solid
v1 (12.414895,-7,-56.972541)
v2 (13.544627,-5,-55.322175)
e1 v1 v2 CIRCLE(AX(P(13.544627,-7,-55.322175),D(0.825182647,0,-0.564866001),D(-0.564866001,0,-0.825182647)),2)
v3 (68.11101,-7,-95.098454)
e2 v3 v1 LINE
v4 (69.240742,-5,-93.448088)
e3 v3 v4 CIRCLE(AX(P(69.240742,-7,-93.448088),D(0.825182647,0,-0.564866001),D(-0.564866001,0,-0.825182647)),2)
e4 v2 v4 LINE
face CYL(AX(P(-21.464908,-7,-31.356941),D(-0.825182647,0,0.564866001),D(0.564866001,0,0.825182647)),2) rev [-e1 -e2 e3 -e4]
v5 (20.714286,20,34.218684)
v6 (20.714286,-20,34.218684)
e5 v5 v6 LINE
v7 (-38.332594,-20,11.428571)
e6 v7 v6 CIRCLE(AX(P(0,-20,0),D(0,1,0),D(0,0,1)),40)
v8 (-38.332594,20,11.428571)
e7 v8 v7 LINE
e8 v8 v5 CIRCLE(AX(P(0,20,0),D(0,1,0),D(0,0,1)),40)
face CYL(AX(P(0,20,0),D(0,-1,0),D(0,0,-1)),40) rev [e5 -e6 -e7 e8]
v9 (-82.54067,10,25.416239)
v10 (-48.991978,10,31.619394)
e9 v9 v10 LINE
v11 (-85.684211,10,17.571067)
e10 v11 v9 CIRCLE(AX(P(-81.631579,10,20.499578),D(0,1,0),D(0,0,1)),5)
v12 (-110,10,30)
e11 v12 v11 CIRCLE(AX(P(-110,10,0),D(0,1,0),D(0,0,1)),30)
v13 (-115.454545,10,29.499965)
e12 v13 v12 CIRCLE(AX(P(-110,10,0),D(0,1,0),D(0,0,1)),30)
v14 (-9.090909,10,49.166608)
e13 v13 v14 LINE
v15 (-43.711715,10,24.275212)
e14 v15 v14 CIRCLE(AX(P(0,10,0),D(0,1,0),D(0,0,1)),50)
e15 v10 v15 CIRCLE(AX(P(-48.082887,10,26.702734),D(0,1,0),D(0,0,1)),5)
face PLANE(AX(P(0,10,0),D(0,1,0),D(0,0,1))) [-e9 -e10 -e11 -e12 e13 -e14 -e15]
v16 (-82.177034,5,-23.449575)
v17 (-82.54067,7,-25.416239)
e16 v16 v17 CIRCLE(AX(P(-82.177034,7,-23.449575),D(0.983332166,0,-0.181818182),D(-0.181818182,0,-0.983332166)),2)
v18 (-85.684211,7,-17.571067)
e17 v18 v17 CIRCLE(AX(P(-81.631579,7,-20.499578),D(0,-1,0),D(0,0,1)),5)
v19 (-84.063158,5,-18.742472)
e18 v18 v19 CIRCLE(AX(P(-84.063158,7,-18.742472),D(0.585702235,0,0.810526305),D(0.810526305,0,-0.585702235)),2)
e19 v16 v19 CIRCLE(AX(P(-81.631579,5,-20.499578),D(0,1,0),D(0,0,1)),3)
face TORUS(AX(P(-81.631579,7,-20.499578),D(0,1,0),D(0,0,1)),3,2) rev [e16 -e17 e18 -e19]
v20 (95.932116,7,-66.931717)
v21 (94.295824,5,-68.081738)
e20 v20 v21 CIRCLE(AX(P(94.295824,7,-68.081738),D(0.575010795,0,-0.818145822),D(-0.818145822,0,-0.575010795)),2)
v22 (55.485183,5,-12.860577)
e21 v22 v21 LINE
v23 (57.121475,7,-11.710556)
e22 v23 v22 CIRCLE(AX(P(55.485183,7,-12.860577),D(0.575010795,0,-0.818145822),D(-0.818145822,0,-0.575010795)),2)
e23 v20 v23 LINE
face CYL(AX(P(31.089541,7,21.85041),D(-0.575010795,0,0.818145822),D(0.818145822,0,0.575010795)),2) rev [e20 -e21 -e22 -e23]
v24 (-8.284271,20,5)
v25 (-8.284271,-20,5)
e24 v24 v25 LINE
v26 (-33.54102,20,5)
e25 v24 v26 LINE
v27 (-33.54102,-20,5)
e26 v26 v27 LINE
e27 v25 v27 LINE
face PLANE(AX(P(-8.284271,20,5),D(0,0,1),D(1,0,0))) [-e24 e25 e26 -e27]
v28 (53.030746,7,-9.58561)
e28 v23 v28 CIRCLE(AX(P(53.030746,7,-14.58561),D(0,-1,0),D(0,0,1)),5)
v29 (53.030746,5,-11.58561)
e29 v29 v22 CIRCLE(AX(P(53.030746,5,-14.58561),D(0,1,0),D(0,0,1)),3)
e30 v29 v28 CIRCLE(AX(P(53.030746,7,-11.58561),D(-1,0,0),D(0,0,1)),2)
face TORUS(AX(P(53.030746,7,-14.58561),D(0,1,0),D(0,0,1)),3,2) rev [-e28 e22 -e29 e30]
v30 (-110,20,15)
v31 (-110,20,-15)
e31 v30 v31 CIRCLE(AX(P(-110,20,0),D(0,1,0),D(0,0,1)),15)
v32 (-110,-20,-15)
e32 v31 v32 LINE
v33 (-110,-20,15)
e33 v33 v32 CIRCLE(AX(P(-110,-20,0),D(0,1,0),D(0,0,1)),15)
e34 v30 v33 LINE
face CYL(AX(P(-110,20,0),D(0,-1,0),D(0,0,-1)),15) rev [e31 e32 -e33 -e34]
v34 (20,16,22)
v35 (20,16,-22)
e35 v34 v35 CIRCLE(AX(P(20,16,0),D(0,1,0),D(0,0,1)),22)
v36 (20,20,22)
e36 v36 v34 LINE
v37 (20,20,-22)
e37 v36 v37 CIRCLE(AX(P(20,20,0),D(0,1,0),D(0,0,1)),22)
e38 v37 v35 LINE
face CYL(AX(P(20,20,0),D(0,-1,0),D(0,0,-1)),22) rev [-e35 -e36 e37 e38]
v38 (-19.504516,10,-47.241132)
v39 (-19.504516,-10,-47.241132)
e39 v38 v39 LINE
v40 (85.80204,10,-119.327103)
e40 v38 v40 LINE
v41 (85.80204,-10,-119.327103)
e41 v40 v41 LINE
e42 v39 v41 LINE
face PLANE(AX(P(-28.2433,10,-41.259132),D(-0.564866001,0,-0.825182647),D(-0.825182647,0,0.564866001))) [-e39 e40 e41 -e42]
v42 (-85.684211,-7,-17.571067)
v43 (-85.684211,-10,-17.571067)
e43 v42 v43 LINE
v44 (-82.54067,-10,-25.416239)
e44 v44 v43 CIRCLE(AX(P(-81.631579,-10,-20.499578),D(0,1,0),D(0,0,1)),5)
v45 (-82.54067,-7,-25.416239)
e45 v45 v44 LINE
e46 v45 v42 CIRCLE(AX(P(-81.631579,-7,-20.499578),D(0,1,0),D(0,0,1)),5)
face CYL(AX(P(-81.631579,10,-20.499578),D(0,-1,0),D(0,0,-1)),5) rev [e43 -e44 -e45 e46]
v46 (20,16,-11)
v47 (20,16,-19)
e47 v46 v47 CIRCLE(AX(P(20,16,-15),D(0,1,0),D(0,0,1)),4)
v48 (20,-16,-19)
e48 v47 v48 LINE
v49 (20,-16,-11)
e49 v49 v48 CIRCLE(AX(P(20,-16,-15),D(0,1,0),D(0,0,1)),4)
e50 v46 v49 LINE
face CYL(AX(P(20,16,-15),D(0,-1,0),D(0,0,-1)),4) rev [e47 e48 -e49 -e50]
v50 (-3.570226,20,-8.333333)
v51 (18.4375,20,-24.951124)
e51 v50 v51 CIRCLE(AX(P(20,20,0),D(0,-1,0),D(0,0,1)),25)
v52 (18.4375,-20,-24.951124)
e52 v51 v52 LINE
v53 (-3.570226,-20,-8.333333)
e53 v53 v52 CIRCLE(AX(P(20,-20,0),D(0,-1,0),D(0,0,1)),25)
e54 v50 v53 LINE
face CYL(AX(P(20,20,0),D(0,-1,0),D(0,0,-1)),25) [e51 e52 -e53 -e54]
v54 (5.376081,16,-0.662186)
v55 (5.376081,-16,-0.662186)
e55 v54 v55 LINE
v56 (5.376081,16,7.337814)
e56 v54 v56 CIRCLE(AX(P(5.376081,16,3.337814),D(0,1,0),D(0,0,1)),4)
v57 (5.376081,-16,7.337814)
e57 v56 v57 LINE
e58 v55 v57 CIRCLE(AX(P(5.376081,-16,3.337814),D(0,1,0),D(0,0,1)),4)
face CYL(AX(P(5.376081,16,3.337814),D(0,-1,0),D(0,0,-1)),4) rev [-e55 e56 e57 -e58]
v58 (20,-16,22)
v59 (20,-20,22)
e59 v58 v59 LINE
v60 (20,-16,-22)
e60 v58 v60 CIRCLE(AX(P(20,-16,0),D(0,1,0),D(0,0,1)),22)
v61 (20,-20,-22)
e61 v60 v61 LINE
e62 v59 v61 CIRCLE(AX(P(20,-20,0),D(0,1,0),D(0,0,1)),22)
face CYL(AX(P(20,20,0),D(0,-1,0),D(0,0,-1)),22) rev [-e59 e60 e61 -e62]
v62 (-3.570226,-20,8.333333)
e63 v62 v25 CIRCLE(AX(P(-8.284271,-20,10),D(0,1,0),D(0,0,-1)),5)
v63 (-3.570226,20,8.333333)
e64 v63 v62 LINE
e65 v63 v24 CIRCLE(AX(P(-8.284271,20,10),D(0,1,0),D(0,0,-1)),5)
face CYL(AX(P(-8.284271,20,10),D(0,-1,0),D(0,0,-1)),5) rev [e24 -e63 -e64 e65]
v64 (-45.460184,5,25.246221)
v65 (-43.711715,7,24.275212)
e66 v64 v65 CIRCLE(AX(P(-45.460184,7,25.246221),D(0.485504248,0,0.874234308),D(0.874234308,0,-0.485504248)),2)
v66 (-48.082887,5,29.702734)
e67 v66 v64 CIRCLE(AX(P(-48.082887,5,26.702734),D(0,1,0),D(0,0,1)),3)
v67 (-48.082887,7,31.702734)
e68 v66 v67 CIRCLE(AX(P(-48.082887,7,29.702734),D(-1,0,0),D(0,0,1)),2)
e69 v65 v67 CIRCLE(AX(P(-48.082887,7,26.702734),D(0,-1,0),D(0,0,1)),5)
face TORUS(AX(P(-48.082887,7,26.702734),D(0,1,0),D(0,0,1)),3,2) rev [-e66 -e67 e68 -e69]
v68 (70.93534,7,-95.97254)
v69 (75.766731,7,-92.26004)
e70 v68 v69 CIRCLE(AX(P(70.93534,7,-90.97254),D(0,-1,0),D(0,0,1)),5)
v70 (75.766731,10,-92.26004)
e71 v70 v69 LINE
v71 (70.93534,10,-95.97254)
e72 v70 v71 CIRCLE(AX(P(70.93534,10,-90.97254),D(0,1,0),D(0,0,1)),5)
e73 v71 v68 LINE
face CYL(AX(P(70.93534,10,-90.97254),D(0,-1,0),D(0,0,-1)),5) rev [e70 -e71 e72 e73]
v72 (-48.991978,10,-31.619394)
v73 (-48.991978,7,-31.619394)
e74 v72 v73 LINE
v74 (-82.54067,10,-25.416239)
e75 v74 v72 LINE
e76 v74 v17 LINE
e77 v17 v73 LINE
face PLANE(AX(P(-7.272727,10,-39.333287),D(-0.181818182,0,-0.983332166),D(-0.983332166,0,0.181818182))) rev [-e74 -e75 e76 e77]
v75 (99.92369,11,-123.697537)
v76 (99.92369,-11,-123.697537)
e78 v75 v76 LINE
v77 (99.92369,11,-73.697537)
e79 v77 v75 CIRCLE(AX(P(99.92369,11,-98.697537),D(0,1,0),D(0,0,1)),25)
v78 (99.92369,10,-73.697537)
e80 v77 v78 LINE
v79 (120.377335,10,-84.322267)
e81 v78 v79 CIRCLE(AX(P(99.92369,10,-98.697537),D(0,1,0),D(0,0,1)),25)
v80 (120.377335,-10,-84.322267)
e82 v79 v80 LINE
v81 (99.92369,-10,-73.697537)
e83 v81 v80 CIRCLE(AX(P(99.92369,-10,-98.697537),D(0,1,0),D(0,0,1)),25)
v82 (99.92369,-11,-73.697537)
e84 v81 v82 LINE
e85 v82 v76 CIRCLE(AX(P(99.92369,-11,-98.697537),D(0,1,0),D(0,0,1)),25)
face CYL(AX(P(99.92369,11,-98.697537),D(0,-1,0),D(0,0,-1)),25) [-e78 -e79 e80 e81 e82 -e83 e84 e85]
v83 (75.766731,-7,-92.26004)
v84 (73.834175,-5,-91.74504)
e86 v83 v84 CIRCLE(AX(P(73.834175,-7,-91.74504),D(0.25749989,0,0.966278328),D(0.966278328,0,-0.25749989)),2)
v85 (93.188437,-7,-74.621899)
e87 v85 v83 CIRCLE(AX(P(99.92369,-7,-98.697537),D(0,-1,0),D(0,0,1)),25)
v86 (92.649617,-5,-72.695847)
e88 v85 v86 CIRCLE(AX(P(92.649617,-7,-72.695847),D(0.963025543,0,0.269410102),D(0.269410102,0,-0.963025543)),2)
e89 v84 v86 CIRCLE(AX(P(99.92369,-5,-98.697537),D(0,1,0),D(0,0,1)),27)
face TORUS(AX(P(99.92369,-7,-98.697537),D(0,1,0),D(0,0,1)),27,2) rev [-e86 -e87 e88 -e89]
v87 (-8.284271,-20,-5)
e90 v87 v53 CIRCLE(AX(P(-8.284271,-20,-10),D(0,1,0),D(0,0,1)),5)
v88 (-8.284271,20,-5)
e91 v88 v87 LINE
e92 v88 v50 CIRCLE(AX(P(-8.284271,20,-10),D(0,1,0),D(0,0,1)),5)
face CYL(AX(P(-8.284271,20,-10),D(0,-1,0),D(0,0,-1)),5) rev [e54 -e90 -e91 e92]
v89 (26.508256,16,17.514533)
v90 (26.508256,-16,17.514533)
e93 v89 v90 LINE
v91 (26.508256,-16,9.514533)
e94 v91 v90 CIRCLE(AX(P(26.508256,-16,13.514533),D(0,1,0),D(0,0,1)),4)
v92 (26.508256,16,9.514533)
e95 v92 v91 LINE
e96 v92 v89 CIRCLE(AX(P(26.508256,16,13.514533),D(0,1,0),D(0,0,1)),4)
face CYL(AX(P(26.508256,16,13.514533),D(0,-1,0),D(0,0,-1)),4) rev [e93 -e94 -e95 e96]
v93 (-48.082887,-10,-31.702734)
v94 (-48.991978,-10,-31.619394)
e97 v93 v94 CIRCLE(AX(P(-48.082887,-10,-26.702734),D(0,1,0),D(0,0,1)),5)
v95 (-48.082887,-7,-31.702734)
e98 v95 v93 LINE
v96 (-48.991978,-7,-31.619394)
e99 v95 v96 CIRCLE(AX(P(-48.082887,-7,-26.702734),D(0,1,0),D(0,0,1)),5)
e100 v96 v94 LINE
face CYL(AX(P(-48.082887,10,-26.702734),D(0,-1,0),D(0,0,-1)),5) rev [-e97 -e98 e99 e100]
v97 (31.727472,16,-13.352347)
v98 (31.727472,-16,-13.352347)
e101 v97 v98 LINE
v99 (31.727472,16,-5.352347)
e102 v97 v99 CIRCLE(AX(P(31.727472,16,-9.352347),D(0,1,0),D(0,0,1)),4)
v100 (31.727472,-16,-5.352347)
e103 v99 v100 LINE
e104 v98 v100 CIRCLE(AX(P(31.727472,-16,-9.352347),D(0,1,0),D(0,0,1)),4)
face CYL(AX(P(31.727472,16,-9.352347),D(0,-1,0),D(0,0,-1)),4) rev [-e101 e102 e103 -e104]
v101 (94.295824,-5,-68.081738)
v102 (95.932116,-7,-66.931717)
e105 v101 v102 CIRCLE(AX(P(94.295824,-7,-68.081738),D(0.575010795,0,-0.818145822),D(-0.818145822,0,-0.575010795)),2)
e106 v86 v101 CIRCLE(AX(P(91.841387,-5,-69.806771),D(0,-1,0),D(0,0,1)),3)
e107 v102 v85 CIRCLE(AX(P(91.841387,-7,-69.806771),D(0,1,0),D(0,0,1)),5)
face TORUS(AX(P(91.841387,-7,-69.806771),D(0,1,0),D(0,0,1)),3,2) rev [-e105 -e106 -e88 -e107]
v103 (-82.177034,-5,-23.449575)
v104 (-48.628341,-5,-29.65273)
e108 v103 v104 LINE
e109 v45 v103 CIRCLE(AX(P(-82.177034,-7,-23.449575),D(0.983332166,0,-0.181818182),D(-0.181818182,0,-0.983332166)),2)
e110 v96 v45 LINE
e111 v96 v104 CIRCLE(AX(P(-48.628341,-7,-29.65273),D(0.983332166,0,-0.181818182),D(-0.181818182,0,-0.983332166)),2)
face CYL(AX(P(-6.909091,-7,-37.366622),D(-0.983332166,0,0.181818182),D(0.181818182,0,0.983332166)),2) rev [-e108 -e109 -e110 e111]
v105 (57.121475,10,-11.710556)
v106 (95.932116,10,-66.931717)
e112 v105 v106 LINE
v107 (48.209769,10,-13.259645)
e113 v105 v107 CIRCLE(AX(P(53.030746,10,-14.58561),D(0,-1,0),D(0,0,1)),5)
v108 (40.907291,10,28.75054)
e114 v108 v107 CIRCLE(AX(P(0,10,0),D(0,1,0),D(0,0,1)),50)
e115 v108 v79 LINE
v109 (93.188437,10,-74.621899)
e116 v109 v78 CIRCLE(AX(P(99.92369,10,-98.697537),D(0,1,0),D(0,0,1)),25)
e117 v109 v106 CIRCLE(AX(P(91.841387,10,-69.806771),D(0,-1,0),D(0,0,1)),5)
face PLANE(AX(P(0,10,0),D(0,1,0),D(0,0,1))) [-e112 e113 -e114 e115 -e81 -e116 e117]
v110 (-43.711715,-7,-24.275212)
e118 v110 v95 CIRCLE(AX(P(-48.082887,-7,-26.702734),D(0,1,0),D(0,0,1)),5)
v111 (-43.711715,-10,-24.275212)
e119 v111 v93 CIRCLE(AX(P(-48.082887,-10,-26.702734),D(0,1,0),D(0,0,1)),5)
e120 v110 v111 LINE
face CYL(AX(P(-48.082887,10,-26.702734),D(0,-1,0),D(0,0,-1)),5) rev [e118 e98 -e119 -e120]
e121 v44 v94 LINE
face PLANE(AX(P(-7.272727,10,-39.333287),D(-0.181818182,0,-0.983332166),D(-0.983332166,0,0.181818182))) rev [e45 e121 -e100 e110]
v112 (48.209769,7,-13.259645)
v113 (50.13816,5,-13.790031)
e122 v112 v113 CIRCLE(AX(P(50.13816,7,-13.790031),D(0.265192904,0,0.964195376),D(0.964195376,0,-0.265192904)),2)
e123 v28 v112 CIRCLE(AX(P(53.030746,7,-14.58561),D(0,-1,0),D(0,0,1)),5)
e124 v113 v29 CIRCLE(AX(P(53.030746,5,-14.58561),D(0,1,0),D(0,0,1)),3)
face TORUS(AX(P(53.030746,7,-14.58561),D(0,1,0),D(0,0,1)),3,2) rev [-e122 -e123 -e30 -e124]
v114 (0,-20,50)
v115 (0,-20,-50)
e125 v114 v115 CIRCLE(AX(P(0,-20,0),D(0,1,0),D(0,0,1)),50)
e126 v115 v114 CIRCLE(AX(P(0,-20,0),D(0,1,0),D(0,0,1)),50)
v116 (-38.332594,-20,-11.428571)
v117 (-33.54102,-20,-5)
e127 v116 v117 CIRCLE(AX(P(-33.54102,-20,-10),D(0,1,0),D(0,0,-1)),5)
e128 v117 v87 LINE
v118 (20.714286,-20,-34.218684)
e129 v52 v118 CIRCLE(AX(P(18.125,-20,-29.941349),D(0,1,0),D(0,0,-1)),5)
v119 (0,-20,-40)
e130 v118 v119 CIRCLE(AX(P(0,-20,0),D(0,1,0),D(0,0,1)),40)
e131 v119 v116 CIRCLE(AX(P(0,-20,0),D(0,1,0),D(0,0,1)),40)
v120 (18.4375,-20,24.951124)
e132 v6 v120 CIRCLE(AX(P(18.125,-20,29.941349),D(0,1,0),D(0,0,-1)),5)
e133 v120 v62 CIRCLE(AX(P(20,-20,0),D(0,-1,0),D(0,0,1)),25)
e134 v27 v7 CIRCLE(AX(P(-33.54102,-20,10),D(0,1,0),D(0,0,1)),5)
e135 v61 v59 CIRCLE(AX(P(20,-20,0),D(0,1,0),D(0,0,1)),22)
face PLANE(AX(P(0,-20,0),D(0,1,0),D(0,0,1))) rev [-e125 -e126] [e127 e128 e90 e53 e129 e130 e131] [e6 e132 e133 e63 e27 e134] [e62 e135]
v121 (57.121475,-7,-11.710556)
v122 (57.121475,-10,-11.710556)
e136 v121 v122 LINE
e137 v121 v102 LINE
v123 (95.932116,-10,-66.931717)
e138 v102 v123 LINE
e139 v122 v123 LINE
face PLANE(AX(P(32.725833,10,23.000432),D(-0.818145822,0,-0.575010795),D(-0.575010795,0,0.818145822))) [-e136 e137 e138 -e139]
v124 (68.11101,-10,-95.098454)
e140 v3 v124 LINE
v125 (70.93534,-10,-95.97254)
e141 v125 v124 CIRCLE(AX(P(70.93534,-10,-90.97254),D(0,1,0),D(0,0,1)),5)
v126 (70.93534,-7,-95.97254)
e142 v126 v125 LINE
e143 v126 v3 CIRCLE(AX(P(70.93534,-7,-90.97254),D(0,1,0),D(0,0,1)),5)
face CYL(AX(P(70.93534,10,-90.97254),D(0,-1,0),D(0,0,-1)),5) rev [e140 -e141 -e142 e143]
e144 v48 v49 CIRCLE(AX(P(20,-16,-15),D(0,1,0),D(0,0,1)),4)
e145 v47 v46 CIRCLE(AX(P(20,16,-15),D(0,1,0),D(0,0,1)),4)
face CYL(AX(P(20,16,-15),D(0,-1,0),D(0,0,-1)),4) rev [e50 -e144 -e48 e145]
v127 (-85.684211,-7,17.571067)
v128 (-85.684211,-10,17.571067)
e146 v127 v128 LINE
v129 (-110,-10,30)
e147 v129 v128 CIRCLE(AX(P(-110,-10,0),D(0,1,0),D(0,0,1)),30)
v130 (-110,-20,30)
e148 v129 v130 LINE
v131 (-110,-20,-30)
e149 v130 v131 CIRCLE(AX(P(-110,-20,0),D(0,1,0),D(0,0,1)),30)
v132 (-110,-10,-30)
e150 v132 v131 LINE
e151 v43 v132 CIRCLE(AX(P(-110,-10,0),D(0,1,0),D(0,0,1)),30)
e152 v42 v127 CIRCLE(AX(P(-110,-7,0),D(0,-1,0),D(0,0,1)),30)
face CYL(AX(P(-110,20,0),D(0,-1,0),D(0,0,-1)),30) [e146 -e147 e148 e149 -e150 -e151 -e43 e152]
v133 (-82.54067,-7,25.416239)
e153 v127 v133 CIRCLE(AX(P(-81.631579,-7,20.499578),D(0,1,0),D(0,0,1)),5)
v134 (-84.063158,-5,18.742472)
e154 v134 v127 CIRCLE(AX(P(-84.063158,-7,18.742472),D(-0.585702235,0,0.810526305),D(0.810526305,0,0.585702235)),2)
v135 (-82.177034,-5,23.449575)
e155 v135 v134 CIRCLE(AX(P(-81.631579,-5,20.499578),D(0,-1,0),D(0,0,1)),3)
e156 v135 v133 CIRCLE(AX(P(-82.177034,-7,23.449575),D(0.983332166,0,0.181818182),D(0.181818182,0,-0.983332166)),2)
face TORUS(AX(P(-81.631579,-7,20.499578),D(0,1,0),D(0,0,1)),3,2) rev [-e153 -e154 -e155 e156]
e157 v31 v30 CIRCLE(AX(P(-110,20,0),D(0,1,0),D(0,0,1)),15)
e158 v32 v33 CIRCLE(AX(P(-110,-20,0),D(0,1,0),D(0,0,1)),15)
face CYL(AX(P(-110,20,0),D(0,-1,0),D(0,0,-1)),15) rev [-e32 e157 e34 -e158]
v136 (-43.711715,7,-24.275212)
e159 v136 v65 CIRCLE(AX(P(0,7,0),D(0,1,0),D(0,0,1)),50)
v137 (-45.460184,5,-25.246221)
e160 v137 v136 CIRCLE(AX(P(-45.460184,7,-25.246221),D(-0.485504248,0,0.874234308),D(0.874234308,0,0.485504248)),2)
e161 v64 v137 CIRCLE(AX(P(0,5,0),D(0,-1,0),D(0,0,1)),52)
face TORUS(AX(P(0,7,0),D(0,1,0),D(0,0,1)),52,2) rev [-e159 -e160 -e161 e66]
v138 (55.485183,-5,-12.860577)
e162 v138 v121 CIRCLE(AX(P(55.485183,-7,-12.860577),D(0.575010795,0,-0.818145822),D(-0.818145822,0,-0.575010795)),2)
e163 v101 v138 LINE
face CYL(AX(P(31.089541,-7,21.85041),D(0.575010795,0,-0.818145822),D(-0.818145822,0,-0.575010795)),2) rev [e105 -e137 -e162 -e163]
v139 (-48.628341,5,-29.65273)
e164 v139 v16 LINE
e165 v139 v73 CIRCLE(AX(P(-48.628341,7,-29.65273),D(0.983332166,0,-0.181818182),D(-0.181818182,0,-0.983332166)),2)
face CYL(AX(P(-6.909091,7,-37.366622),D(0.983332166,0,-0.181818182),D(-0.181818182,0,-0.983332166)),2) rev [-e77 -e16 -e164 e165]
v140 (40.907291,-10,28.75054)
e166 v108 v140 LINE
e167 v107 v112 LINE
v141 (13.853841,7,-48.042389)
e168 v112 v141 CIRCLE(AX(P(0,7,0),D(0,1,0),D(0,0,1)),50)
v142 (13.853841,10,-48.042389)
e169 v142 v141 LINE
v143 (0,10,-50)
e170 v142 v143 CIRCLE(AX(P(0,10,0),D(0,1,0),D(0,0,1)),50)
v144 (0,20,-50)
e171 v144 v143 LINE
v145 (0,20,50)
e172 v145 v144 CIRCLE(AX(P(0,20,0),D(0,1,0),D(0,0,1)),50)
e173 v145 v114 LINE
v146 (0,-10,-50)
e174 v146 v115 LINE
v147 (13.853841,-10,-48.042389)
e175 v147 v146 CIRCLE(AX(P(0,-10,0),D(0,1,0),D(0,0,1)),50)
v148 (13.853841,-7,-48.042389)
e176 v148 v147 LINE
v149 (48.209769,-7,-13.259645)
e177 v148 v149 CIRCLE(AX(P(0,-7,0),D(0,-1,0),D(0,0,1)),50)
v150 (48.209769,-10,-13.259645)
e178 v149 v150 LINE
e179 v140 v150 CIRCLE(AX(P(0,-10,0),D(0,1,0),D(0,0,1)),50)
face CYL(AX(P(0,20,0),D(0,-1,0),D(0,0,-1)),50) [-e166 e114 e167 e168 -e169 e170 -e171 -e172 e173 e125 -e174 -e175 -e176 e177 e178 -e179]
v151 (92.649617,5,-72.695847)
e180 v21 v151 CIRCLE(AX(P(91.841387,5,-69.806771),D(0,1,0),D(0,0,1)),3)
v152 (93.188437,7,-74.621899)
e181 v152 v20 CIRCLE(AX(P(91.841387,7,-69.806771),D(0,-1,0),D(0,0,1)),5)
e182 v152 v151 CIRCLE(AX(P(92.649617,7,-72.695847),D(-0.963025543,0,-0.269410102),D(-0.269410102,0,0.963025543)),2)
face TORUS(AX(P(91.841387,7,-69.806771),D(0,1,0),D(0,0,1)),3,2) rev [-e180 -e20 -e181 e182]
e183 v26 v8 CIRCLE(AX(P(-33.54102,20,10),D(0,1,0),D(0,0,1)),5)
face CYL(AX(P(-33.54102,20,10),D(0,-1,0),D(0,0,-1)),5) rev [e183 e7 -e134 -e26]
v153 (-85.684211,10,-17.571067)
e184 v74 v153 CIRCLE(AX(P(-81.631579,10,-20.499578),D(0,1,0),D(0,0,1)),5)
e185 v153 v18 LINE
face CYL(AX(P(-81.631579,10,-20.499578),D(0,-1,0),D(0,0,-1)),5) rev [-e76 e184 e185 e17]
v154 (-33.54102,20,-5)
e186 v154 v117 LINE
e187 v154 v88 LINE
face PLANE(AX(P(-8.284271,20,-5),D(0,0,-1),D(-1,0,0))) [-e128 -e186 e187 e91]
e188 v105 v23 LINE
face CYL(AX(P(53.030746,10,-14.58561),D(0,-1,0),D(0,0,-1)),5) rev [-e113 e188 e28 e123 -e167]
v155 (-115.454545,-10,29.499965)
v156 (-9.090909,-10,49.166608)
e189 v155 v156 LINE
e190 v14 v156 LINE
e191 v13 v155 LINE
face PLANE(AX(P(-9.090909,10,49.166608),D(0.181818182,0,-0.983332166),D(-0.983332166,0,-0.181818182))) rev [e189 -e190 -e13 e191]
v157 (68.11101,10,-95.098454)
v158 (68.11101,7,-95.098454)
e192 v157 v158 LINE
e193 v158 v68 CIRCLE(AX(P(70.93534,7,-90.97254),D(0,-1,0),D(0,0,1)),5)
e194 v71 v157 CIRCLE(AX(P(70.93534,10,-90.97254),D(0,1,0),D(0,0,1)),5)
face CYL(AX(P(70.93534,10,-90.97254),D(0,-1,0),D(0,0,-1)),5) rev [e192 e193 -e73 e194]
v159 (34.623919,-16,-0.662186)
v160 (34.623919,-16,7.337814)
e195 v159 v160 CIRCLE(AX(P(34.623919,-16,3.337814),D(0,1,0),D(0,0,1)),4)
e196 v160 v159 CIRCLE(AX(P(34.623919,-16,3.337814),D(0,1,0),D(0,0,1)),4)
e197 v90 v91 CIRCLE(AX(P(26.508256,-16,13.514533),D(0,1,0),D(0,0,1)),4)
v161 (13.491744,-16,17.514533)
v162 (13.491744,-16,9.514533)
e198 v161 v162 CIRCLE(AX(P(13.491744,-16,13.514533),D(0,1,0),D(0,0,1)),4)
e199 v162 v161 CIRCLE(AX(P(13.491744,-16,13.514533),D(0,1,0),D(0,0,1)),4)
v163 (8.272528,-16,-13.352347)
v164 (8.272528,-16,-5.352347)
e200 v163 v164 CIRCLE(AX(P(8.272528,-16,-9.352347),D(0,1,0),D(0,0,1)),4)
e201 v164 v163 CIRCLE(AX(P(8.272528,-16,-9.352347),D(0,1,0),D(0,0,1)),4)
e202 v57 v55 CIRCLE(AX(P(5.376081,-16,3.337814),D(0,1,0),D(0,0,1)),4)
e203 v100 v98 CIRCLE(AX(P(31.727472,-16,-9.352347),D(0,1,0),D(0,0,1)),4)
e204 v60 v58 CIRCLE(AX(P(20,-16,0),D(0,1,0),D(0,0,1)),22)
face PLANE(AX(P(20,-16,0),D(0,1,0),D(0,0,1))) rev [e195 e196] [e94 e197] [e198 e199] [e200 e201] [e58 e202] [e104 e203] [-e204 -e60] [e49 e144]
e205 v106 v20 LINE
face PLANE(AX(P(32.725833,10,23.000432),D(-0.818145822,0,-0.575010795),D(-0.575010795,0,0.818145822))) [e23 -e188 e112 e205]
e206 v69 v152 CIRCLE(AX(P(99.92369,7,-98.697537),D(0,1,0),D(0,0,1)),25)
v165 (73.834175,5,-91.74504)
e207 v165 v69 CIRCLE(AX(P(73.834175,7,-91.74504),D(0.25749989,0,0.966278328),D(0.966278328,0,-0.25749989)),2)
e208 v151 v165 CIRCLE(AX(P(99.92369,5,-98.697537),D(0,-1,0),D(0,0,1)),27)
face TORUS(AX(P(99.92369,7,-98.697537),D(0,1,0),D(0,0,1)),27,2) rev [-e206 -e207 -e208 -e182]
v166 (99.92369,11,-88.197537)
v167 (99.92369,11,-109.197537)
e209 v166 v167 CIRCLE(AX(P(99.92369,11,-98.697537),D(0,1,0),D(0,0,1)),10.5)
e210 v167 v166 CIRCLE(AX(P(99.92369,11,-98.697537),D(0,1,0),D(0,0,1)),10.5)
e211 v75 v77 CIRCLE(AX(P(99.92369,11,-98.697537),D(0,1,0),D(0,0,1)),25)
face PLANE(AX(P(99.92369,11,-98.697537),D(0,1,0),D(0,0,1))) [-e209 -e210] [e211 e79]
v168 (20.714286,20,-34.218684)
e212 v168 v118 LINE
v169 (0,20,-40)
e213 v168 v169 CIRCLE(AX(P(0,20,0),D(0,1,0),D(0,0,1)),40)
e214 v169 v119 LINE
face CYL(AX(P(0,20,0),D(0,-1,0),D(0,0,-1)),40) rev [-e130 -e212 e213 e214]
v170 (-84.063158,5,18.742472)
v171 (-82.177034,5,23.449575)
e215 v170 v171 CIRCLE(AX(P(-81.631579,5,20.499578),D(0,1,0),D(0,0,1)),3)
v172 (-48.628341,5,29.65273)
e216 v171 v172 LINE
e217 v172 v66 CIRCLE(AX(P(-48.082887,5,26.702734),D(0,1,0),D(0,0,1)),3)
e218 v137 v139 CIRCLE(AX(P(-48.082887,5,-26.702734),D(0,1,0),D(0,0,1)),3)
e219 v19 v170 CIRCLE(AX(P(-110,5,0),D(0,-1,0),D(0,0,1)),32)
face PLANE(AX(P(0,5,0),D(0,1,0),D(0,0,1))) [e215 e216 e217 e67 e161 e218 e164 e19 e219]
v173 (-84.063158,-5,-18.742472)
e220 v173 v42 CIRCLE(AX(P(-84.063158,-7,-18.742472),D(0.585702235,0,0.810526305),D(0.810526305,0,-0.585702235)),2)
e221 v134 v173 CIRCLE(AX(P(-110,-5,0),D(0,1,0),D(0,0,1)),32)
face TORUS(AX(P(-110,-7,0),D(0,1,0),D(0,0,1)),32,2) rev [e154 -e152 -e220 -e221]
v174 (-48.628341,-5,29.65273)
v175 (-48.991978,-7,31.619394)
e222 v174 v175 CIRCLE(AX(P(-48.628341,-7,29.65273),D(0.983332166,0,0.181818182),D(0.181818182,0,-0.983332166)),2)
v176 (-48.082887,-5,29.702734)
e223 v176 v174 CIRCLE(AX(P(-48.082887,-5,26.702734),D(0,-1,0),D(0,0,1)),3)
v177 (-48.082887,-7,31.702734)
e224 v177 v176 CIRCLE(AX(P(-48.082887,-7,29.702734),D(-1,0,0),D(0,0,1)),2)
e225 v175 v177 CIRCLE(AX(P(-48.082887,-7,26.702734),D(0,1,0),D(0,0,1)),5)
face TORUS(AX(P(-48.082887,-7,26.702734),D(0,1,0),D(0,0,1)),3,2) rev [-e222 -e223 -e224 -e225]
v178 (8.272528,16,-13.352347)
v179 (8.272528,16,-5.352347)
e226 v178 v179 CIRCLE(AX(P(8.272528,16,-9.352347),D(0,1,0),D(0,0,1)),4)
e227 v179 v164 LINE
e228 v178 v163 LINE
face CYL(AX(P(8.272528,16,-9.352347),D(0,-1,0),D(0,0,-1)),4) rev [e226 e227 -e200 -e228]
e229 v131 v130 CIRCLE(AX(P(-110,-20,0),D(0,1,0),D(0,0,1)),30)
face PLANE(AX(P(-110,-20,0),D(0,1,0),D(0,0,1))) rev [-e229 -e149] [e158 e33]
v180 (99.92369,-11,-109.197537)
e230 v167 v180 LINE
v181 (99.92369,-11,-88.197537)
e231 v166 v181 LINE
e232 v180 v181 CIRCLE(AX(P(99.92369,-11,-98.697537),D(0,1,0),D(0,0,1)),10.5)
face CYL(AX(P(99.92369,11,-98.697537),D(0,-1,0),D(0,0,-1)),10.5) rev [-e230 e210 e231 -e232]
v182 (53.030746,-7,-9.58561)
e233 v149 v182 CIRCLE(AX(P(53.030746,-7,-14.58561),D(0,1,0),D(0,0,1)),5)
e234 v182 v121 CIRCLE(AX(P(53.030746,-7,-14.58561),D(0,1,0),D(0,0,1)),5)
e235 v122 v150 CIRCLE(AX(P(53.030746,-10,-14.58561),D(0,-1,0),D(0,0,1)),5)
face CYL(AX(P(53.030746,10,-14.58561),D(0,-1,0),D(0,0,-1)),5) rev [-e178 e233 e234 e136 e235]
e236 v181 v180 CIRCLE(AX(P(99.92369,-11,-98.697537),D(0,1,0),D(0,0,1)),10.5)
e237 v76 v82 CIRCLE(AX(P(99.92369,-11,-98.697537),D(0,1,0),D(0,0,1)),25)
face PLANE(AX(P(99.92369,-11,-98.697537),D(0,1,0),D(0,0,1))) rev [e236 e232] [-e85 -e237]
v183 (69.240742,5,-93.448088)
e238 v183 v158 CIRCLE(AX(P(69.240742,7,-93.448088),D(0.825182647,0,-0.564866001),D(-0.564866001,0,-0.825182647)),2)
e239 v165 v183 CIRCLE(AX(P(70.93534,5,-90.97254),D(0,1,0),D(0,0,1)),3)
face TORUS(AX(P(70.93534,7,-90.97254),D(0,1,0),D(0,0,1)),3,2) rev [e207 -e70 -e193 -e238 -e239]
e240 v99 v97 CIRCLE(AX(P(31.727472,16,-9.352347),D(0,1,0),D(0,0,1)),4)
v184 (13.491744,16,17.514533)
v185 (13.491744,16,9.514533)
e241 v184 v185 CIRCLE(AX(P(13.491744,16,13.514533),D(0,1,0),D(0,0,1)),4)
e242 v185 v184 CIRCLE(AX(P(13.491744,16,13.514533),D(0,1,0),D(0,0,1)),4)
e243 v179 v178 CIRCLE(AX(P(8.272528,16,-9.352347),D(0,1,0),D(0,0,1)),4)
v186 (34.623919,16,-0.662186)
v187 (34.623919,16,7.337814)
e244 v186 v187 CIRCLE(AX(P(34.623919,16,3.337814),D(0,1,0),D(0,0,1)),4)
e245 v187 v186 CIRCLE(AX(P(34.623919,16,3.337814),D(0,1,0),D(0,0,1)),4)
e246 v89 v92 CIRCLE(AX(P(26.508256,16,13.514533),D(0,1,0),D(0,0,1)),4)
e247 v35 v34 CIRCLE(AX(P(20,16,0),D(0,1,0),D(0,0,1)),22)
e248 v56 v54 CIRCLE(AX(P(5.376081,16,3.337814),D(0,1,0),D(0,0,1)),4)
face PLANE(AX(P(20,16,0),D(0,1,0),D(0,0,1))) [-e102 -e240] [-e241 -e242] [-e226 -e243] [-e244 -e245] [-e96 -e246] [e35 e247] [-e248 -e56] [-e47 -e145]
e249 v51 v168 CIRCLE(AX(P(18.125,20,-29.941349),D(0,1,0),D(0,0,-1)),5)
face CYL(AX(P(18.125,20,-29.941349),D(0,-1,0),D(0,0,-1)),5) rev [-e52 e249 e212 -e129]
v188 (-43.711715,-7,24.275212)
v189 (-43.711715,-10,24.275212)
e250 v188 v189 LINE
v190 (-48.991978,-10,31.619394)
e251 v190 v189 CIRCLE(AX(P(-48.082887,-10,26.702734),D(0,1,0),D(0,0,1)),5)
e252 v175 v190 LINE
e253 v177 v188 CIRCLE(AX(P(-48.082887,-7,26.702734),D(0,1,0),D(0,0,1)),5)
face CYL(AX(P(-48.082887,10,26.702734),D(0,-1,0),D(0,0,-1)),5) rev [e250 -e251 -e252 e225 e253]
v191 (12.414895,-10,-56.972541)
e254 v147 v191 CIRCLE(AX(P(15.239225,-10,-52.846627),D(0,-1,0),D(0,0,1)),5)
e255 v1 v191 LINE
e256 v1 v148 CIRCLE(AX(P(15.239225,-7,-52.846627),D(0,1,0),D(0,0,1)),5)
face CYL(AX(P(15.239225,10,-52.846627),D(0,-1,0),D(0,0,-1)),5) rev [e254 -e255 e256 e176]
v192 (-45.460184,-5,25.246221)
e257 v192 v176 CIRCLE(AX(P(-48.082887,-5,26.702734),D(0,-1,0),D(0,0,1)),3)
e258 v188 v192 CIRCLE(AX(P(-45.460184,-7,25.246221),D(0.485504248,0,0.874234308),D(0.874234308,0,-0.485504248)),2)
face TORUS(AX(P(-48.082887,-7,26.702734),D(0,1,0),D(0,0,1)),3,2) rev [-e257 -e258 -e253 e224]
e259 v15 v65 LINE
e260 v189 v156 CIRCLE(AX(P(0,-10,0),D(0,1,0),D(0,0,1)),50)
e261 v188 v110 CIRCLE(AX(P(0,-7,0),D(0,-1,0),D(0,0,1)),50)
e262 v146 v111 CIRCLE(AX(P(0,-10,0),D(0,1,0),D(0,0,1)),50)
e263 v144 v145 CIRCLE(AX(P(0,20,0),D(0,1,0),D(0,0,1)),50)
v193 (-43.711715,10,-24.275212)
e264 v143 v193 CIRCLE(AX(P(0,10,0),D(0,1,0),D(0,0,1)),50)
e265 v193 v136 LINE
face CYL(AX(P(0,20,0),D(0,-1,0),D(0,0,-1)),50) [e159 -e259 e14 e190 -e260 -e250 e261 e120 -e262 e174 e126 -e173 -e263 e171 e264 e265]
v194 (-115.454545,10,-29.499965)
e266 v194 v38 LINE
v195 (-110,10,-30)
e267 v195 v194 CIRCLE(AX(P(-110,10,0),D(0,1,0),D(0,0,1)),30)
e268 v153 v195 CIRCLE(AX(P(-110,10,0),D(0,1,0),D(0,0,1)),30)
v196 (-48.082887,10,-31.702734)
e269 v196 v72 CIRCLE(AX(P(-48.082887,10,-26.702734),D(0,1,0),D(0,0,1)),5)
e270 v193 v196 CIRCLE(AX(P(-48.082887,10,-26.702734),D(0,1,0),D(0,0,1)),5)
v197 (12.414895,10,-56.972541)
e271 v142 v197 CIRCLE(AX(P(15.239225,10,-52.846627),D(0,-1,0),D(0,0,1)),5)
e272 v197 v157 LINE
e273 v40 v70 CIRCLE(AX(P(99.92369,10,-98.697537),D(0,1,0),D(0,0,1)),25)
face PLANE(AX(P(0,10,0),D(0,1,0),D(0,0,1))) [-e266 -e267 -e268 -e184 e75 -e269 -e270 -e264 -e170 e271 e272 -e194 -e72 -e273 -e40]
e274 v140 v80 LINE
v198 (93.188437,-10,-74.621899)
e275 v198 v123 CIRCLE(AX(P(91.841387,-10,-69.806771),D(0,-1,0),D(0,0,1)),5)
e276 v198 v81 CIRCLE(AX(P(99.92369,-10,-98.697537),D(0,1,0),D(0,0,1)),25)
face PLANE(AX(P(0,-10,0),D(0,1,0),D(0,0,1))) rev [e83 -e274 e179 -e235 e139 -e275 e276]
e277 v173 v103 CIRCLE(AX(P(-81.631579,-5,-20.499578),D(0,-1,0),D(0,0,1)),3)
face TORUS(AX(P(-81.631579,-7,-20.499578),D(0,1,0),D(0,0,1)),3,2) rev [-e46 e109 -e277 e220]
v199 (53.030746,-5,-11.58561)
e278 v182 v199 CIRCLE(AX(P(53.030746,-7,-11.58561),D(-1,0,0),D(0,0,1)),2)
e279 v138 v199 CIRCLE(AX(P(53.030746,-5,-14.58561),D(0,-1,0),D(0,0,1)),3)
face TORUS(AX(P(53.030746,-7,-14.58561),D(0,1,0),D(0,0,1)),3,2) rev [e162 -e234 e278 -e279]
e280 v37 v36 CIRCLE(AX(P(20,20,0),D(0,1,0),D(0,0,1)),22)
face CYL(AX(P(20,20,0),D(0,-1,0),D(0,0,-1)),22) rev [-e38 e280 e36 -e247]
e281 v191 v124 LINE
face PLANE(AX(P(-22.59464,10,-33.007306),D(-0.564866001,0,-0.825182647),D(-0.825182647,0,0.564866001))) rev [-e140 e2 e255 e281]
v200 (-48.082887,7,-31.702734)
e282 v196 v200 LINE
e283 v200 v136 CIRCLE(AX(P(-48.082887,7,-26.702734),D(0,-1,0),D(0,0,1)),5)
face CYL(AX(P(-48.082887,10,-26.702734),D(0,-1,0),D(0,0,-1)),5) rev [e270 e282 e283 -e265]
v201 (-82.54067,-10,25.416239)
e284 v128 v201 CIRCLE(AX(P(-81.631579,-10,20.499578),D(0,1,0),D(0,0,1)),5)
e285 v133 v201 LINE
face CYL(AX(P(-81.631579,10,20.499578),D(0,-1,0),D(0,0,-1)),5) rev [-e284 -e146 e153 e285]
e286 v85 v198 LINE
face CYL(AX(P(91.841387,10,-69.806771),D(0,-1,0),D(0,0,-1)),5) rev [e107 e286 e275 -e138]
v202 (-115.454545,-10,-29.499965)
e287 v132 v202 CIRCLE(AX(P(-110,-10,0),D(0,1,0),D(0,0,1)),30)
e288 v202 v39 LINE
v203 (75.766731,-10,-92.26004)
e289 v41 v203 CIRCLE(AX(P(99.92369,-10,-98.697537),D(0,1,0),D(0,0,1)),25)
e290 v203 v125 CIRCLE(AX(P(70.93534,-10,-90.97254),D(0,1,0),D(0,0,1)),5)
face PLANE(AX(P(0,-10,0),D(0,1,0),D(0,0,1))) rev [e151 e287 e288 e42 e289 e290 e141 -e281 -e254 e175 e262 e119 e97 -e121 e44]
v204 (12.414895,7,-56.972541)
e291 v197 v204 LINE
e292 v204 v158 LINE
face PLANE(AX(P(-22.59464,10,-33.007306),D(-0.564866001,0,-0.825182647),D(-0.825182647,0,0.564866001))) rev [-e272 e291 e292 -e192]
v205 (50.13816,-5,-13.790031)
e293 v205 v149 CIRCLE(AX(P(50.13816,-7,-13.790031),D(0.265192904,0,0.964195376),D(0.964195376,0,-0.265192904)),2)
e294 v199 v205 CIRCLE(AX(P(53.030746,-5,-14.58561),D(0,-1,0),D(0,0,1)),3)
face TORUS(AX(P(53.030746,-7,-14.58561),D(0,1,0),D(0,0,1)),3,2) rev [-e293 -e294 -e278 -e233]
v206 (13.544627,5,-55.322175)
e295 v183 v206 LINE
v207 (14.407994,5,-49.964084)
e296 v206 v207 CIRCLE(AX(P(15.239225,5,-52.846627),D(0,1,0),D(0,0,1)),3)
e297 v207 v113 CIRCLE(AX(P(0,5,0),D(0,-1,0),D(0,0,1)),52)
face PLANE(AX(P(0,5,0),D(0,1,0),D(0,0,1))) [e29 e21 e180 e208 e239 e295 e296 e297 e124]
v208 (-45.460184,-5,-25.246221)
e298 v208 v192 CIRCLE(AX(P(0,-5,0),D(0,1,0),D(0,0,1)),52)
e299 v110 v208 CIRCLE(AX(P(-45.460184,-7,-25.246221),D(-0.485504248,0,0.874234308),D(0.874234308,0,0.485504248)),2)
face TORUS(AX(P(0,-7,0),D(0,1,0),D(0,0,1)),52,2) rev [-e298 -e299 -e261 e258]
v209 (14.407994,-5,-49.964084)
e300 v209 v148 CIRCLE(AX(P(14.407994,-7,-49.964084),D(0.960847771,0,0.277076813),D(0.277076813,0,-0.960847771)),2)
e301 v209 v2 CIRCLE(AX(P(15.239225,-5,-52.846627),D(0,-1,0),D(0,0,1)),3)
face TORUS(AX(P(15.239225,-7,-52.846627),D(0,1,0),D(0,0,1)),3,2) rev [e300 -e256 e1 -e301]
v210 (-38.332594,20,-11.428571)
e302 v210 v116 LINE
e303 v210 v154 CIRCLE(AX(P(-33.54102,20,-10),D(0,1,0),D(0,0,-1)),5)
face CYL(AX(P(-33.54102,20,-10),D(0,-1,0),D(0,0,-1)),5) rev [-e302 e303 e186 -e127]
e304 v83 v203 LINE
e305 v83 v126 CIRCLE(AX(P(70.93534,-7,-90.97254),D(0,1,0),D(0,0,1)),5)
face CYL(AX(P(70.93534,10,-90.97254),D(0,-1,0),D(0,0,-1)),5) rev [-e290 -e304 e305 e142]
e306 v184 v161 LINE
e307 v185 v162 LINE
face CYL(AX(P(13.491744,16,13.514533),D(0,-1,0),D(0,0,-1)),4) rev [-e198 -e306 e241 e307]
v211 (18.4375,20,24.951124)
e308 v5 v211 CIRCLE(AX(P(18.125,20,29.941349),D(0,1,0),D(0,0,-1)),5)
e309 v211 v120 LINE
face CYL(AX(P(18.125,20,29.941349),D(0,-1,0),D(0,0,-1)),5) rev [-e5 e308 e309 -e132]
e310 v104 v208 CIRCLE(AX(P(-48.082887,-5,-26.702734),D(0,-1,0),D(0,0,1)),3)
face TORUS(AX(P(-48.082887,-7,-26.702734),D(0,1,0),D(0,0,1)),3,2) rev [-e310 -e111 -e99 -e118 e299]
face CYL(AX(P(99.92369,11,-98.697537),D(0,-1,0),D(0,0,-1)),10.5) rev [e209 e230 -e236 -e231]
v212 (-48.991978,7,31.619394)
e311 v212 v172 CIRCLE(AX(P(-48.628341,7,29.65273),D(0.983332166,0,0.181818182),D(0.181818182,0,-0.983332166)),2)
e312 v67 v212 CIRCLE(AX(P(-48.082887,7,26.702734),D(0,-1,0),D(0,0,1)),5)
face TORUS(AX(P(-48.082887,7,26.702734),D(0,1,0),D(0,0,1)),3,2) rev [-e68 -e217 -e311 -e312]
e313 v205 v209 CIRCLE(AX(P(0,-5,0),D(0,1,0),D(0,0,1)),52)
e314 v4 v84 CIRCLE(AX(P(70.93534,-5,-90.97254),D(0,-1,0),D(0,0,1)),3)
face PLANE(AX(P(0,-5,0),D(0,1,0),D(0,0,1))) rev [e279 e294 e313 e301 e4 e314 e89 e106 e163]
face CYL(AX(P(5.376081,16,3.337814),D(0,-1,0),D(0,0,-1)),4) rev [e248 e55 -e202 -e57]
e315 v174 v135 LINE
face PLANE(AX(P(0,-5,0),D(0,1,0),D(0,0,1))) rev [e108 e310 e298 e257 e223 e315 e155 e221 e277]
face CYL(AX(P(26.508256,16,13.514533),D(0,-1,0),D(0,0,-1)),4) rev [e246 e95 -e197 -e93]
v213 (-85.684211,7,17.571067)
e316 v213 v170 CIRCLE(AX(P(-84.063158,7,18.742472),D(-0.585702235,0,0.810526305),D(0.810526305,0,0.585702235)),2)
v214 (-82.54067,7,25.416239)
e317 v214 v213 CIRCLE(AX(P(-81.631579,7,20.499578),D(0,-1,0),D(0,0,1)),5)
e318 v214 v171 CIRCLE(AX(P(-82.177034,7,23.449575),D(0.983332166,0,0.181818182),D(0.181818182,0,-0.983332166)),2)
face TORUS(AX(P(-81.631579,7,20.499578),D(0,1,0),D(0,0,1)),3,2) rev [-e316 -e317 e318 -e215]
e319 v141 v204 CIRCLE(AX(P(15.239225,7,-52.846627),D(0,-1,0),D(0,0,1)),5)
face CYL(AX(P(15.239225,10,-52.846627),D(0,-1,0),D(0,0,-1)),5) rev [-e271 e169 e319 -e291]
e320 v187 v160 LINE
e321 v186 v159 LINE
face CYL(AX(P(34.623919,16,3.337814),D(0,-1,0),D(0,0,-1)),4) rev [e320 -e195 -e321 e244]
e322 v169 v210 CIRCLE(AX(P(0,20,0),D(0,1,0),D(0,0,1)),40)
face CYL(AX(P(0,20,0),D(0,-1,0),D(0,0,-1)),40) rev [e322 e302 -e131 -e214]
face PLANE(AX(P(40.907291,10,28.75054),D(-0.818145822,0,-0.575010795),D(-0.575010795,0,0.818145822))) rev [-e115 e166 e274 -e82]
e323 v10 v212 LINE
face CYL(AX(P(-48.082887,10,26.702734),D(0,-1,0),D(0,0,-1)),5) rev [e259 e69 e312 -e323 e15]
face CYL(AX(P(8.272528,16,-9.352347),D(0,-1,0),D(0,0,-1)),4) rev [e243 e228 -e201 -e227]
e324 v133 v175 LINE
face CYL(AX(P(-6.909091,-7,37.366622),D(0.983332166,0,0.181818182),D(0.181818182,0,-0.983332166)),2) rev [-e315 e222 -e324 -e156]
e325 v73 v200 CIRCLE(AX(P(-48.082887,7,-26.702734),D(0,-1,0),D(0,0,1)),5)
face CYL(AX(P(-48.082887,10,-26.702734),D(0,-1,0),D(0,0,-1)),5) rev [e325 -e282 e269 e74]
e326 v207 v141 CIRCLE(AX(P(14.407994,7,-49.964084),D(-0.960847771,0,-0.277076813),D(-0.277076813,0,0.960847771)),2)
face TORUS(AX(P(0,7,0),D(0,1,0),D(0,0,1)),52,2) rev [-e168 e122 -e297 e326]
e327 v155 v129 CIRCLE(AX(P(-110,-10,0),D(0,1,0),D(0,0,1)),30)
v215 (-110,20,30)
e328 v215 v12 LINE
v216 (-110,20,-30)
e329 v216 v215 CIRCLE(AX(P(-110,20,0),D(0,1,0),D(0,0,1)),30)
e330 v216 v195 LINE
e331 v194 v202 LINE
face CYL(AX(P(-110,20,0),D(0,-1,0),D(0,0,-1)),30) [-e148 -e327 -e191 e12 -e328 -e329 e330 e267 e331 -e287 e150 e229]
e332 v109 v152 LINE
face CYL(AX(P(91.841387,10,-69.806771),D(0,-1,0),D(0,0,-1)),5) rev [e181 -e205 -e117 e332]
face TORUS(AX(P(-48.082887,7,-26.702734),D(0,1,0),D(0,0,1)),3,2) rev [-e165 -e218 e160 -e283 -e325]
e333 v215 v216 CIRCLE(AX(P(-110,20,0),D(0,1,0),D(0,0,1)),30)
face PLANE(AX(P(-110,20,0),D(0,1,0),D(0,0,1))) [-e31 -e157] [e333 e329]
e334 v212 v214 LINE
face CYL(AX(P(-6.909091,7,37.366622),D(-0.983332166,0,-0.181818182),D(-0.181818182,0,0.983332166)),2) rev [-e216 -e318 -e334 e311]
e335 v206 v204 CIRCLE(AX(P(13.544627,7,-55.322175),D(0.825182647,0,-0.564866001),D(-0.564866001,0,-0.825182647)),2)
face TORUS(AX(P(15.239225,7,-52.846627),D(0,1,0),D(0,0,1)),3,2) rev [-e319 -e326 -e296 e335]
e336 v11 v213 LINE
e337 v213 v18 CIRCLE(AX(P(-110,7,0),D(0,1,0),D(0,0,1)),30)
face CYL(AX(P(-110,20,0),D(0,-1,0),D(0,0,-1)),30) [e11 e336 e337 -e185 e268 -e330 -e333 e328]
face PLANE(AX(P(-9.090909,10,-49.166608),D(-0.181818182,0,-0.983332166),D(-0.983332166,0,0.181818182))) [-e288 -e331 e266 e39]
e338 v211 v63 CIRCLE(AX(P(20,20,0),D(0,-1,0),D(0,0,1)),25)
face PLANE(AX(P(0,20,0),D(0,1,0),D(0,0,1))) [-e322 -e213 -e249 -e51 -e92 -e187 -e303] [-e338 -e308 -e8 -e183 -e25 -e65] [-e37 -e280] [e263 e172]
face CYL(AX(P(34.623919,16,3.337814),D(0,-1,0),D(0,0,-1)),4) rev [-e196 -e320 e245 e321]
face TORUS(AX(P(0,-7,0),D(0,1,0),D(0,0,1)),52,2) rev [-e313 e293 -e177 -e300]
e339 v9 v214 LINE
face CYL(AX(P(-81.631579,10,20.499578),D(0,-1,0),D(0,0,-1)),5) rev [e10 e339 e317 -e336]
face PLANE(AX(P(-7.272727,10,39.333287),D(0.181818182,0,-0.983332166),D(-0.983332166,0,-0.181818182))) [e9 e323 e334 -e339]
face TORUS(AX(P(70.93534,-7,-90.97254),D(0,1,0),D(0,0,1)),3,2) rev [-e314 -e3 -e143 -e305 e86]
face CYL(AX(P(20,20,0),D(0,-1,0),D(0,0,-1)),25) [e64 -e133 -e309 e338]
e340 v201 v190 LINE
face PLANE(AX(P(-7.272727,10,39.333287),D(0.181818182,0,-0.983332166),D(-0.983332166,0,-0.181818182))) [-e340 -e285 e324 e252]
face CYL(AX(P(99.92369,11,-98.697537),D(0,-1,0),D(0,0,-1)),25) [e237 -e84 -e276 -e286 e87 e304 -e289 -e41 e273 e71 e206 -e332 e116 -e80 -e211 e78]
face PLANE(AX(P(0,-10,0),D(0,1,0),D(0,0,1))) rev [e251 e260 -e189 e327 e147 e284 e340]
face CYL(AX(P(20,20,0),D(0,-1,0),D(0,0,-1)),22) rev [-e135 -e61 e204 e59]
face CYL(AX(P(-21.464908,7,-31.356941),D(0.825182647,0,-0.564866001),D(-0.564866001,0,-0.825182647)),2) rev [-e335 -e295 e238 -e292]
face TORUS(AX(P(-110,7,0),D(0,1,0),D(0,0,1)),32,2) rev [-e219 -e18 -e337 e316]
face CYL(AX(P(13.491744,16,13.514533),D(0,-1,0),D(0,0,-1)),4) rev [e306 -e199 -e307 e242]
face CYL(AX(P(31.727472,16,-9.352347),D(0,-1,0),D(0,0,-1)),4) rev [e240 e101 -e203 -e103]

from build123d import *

# Parameters (mm, degrees)
BELLCRANK_PROFILE_SKETCH_R   = 50
BELLCRANK_PROFILE_SKETCH_R_2 = 22
BELLCRANK_BODY_DEPTH         = 20
HUB_HOLE_CIRCLE_SKETCH_R     = 22
HUB_HOLE_CIRCLE_SKETCH_R_2   = 4
HUB_HOLES_7X_8_DEPTH         = 16
ARM_A_WEB_SKETCH_R           = 25
ARM_A_WEB_SKETCH_R_2         = 10.5
ARM_A_WEB_DEPTH              = 11
ARM_A_POCKET_DEPTH           = 10
ARM_A_INNER_POCKET_DEPTH     = 5
ARM_A_POCKET_FILLETS_R2_R    = 2
ARM_B_SKETCH_R               = 30
ARM_B_SKETCH_R_2             = 15
ARM_B_DEPTH                  = 20
ARM_B_POCKET_DEPTH           = 10
ARM_B_INNER_POCKET_DEPTH     = 5
ARM_B_POCKET_FILLETS_R2_R    = 2


with BuildPart() as part:
    # Bellcrank Profile Sketch → Bellcrank Body (new, symmetric)
    with BuildSketch(Plane(origin=(0, 0, 0), x_dir=(1, 0, 0), z_dir=(0, 1, 0))):
        with Locations(Location((0, 0, 0), (0, 0, 270))):
            Circle(BELLCRANK_PROFILE_SKETCH_R)
        with Locations(Location((20, 0, 0), (0, 0, 270))):
            Circle(BELLCRANK_PROFILE_SKETCH_R_2, mode=Mode.SUBTRACT)
        with BuildLine():
            Line((-8.284271247, 5), (-33.541019662, 5))
            ThreePointArc((-33.541019662, 5), (-37.549938291, 7.011928477), (-38.3325939, 11.428571429))
            ThreePointArc((-38.3325939, 11.428571429), (-14.403072902, 37.316906235), (20.714285714, 34.218684477))
            ThreePointArc((20.714285714, 34.218684477), (22.980616225, 28.748457023), (18.4375, 24.951124098))
            ThreePointArc((18.4375, 24.951124098), (4.935099668, 19.951159815), (-3.57022604, 8.333333333))
            ThreePointArc((-3.57022604, 8.333333333), (-5.397519902, 5.917517095), (-8.284271247, 5))
        make_face(mode=Mode.SUBTRACT)
        with BuildLine():
            Line((-8.284271247, -5), (-33.541019662, -5))
            ThreePointArc((-33.541019662, -5), (-37.549938291, -7.011928477), (-38.3325939, -11.428571429))
            ThreePointArc((-38.3325939, -11.428571429), (-14.403072902, -37.316906235), (20.714285714, -34.218684477))
            ThreePointArc((20.714285714, -34.218684477), (22.980616225, -28.748457023), (18.4375, -24.951124098))
            ThreePointArc((18.4375, -24.951124098), (4.935099668, -19.951159815), (-3.57022604, -8.333333333))
            ThreePointArc((-3.57022604, -8.333333333), (-5.397519902, -5.917517095), (-8.284271247, -5))
        make_face(mode=Mode.SUBTRACT)
    extrude(amount=BELLCRANK_BODY_DEPTH, both=True)

    # Hub Hole Circle Sketch → Hub Holes 7x_8 (add, symmetric)
    with BuildSketch(Plane(origin=(0, 0, 0), x_dir=(1, 0, 0), z_dir=(0, 1, 0))):
        with Locations(Location((20, 0, 0), (0, 0, 270))):
            Circle(HUB_HOLE_CIRCLE_SKETCH_R)
        with Locations(Location((20, 15, 0), (0, 0, 270))):
            Circle(HUB_HOLE_CIRCLE_SKETCH_R_2, mode=Mode.SUBTRACT)
        with Locations(Location((31.727472237, 9.352347028, 0), (0, 0, 270))):
            Circle(HUB_HOLE_CIRCLE_SKETCH_R_2, mode=Mode.SUBTRACT)
        with Locations(Location((34.623918683, -3.337814009, 0), (0, 0, 270))):
            Circle(HUB_HOLE_CIRCLE_SKETCH_R_2, mode=Mode.SUBTRACT)
        with Locations(Location((26.508256087, -13.514533019, 0), (0, 0, 270))):
            Circle(HUB_HOLE_CIRCLE_SKETCH_R_2, mode=Mode.SUBTRACT)
        with Locations(Location((13.491743913, -13.514533019, 0), (0, 0, 270))):
            Circle(HUB_HOLE_CIRCLE_SKETCH_R_2, mode=Mode.SUBTRACT)
        with Locations(Location((5.376081317, -3.337814009, 0), (0, 0, 270))):
            Circle(HUB_HOLE_CIRCLE_SKETCH_R_2, mode=Mode.SUBTRACT)
        with Locations(Location((8.272527763, 9.352347028, 0), (0, 0, 270))):
            Circle(HUB_HOLE_CIRCLE_SKETCH_R_2, mode=Mode.SUBTRACT)
    extrude(amount=HUB_HOLES_7X_8_DEPTH, both=True)



with BuildPart() as body_2:
    # Arm A Web Sketch → Arm A Web (new, symmetric)
    with BuildSketch(Plane(origin=(0, 0, 0), x_dir=(1, 0, 0), z_dir=(0, 1, 0))):
        with Locations(Location((99.923689663, 98.697537105, 0), (0, 0, 270))):
            Circle(ARM_A_WEB_SKETCH_R)
        with Locations(Location((99.923689663, 98.697537105, 0), (0, 0, 270))):
            Circle(ARM_A_WEB_SKETCH_R_2, mode=Mode.SUBTRACT)
    extrude(amount=ARM_A_WEB_DEPTH, both=True)


with BuildPart() as part_1:
    add(part.part)

    add(body_2.part)  # Arm A Pocket merges body 2
    # Arm A Pocket Sketch → Arm A Pocket (add, symmetric)
    with BuildSketch(Plane(origin=(0, 0, 0), x_dir=(1, 0, 0), z_dir=(0, 1, 0))):
        with BuildLine():
            ThreePointArc((57.121474807, 11.710555748), (52.174454283, 9.659478884), (48.209768815, 13.2596452))
            ThreePointArc((48.209768815, 13.2596452), (49.261308362, -8.562914134), (40.907291105, -28.750539725))
            Line((40.907291105, -28.750539725), (120.377335216, 84.322267243))
            ThreePointArc((120.377335216, 84.322267243), (108.324455399, 75.151260647), (93.188437113, 74.621898524))
            ThreePointArc((93.188437113, 74.621898524), (96.550641894, 71.486923955), (95.932115713, 66.931716835))
            Line((95.932115713, 66.931716835), (57.121474807, 11.710555748))
        make_face()
        with BuildLine():
            Line((85.802039648, 119.327103287), (-28.243300031, 41.259132363))
            ThreePointArc((-28.243300031, 41.259132363), (-7.954072951, 49.363273023), (13.853840649, 48.042388567))
            ThreePointArc((13.853840649, 48.042388567), (10.302897412, 52.051220129), (12.414894711, 56.97254066))
            Line((12.414894711, 56.97254066), (68.11100983, 95.098453634))
            ThreePointArc((68.11100983, 95.098453634), (72.673506196, 95.660693306), (75.766731472, 92.260039849))
            ThreePointArc((75.766731472, 92.260039849), (76.48292512, 107.388368921), (85.802039648, 119.327103287))
        make_face()
    extrude(amount=ARM_A_POCKET_DEPTH, both=True)

    # Sketch4_3 → Arm A Inner Pocket (add, symmetric)
    with BuildSketch(Plane(origin=(0, 0, 0), x_dir=(1, 0, 0), z_dir=(0, 1, 0))):
        with BuildLine():
            ThreePointArc((93.188437113, 74.621898524), (96.550641894, 71.486923955), (95.932115713, 66.931716835))
            Line((95.932115713, 66.931716835), (57.121474807, 11.710555748))
            ThreePointArc((57.121474807, 11.710555748), (52.174454283, 9.659478884), (48.209768815, 13.2596452))
            ThreePointArc((48.209768815, 13.2596452), (35.572921077, 35.136409692), (13.853840649, 48.042388567))
            ThreePointArc((13.853840649, 48.042388567), (10.302897412, 52.051220129), (12.414894711, 56.97254066))
            Line((12.414894711, 56.97254066), (68.11100983, 95.098453634))
            ThreePointArc((68.11100983, 95.098453634), (72.673506196, 95.660693306), (75.766731472, 92.260039849))
            ThreePointArc((75.766731472, 92.260039849), (82.137229125, 81.129332259), (93.188437113, 74.621898524))
        make_face()
    extrude(amount=ARM_A_INNER_POCKET_DEPTH, both=True)

    # Arm A Pocket Fillets R2
    arm_a_pocket_fillets_r2_edges = [part_1.edges().sort_by_distance(p)[0] for p in [
        (96.550641894, 5, -71.486923955),
        (82.137229125, 5, -81.129332259),
        (72.673506196, -5, -95.660693306),
        (40.262952271, 5, -76.035497147),
        (10.302897412, 5, -52.051220129),
        (35.572921077, 5, -35.136409692),
        (52.174454283, 5, -9.659478884),
        (76.52679526, -5, -39.321136292),
        (72.673506196, 5, -95.660693306),
        (76.52679526, 5, -39.321136292),
        (96.550641894, -5, -71.486923955),
        (52.174454283, -5, -9.659478884),
        (35.572921077, -5, -35.136409692),
        (10.302897412, -5, -52.051220129),
        (40.262952271, -5, -76.035497147),
        (82.137229125, -5, -81.129332259),
    ]]
    fillet(arm_a_pocket_fillets_r2_edges, radius=ARM_A_POCKET_FILLETS_R2_R)



with BuildPart() as body_2_2:
    # Arm B Sketch → Arm B (new, symmetric)
    with BuildSketch(Plane(origin=(0, 0, 0), x_dir=(1, 0, 0), z_dir=(0, 1, 0))):
        with Locations(Location((-110, 0, 0), (0, 0, 270))):
            Circle(ARM_B_SKETCH_R)
        with Locations(Location((-110, 0, 0), (0, 0, 270))):
            Circle(ARM_B_SKETCH_R_2, mode=Mode.SUBTRACT)
    extrude(amount=ARM_B_DEPTH, both=True)


with BuildPart() as part_2:
    add(part_1.part)

    add(body_2_2.part)  # Arm B Pocket merges body 2 2
    # Arm B Pocket Sketch → Arm B Pocket (add, symmetric)
    with BuildSketch(Plane(origin=(0, 0, 0), x_dir=(1, 0, 0), z_dir=(0, 1, 0))):
        with BuildLine():
            ThreePointArc((-82.540670225, -25.416239066), (-86.272845666, -22.359321946), (-85.684210842, -17.57106706))
            ThreePointArc((-85.684210842, -17.57106706), (-98.841537744, -27.847598103), (-115.454545455, -29.499964981))
            Line((-115.454545455, -29.499964981), (-9.090909091, -49.166608302))
            ThreePointArc((-9.090909091, -49.166608302), (-29.187748892, -40.596493871), (-43.71171539, -24.275212412))
            ThreePointArc((-43.71171539, -24.275212412), (-44.023237542, -29.621508542), (-48.991977838, -31.619394483))
            Line((-48.991977838, -31.619394483), (-82.540670225, -25.416239066))
        make_face()
        with BuildLine():
            Line((-9.090909091, 49.166608302), (-115.454545455, 29.499964981))
            ThreePointArc((-115.454545455, 29.499964981), (-98.841537744, 27.847598103), (-85.684210842, 17.57106706))
            ThreePointArc((-85.684210842, 17.57106706), (-86.272845666, 22.359321946), (-82.540670225, 25.416239066))
            Line((-82.540670225, 25.416239066), (-48.991977838, 31.619394483))
            ThreePointArc((-48.991977838, 31.619394483), (-44.023237542, 29.621508542), (-43.71171539, 24.275212412))
            ThreePointArc((-43.71171539, 24.275212412), (-29.187748892, 40.596493871), (-9.090909091, 49.166608302))
        make_face()
    extrude(amount=ARM_B_POCKET_DEPTH, both=True)

    # Sketch7_4 → Arm B Inner Pocket (add, symmetric)
    with BuildSketch(Plane(origin=(0, 0, 0), x_dir=(1, 0, 0), z_dir=(0, 1, 0))):
        with BuildLine():
            Line((-82.540670225, 25.416239066), (-48.991977838, 31.619394483))
            ThreePointArc((-48.991977838, 31.619394483), (-44.023237542, 29.621508542), (-43.71171539, 24.275212412))
            ThreePointArc((-43.71171539, 24.275212412), (-50, 0), (-43.71171539, -24.275212412))
            ThreePointArc((-43.71171539, -24.275212412), (-44.023237542, -29.621508542), (-48.991977838, -31.619394483))
            Line((-48.991977838, -31.619394483), (-82.540670225, -25.416239066))
            ThreePointArc((-82.540670225, -25.416239066), (-86.272845666, -22.359321946), (-85.684210842, -17.57106706))
            ThreePointArc((-85.684210842, -17.57106706), (-80, 0), (-85.684210842, 17.57106706))
            ThreePointArc((-85.684210842, 17.57106706), (-86.272845666, 22.359321946), (-82.540670225, 25.416239066))
        make_face()
    extrude(amount=ARM_B_INNER_POCKET_DEPTH, both=True)

    # Arm B Pocket Fillets R2
    arm_b_pocket_fillets_r2_edges = [part_2.edges().sort_by_distance(p)[0] for p in [
        (-65.766324032, 5, -28.517816775),
        (-86.272845666, -5, -22.359321946),
        (-80, 5, 0),
        (-86.272845666, -5, 22.359321946),
        (-65.766324032, -5, 28.517816775),
        (-44.023237542, -5, 29.621508542),
        (-50, 5, 0),
        (-44.023237542, -5, -29.621508542),
        (-86.272845666, 5, -22.359321946),
        (-86.272845666, 5, 22.359321946),
        (-65.766324032, 5, 28.517816775),
        (-44.023237542, 5, 29.621508542),
        (-44.023237542, 5, -29.621508542),
        (-65.766324032, -5, -28.517816775),
        (-50, -5, 0),
        (-80, -5, 0),
    ]]
    fillet(arm_b_pocket_fillets_r2_edges, radius=ARM_B_POCKET_FILLETS_R2_R)


solid = part_2.part
